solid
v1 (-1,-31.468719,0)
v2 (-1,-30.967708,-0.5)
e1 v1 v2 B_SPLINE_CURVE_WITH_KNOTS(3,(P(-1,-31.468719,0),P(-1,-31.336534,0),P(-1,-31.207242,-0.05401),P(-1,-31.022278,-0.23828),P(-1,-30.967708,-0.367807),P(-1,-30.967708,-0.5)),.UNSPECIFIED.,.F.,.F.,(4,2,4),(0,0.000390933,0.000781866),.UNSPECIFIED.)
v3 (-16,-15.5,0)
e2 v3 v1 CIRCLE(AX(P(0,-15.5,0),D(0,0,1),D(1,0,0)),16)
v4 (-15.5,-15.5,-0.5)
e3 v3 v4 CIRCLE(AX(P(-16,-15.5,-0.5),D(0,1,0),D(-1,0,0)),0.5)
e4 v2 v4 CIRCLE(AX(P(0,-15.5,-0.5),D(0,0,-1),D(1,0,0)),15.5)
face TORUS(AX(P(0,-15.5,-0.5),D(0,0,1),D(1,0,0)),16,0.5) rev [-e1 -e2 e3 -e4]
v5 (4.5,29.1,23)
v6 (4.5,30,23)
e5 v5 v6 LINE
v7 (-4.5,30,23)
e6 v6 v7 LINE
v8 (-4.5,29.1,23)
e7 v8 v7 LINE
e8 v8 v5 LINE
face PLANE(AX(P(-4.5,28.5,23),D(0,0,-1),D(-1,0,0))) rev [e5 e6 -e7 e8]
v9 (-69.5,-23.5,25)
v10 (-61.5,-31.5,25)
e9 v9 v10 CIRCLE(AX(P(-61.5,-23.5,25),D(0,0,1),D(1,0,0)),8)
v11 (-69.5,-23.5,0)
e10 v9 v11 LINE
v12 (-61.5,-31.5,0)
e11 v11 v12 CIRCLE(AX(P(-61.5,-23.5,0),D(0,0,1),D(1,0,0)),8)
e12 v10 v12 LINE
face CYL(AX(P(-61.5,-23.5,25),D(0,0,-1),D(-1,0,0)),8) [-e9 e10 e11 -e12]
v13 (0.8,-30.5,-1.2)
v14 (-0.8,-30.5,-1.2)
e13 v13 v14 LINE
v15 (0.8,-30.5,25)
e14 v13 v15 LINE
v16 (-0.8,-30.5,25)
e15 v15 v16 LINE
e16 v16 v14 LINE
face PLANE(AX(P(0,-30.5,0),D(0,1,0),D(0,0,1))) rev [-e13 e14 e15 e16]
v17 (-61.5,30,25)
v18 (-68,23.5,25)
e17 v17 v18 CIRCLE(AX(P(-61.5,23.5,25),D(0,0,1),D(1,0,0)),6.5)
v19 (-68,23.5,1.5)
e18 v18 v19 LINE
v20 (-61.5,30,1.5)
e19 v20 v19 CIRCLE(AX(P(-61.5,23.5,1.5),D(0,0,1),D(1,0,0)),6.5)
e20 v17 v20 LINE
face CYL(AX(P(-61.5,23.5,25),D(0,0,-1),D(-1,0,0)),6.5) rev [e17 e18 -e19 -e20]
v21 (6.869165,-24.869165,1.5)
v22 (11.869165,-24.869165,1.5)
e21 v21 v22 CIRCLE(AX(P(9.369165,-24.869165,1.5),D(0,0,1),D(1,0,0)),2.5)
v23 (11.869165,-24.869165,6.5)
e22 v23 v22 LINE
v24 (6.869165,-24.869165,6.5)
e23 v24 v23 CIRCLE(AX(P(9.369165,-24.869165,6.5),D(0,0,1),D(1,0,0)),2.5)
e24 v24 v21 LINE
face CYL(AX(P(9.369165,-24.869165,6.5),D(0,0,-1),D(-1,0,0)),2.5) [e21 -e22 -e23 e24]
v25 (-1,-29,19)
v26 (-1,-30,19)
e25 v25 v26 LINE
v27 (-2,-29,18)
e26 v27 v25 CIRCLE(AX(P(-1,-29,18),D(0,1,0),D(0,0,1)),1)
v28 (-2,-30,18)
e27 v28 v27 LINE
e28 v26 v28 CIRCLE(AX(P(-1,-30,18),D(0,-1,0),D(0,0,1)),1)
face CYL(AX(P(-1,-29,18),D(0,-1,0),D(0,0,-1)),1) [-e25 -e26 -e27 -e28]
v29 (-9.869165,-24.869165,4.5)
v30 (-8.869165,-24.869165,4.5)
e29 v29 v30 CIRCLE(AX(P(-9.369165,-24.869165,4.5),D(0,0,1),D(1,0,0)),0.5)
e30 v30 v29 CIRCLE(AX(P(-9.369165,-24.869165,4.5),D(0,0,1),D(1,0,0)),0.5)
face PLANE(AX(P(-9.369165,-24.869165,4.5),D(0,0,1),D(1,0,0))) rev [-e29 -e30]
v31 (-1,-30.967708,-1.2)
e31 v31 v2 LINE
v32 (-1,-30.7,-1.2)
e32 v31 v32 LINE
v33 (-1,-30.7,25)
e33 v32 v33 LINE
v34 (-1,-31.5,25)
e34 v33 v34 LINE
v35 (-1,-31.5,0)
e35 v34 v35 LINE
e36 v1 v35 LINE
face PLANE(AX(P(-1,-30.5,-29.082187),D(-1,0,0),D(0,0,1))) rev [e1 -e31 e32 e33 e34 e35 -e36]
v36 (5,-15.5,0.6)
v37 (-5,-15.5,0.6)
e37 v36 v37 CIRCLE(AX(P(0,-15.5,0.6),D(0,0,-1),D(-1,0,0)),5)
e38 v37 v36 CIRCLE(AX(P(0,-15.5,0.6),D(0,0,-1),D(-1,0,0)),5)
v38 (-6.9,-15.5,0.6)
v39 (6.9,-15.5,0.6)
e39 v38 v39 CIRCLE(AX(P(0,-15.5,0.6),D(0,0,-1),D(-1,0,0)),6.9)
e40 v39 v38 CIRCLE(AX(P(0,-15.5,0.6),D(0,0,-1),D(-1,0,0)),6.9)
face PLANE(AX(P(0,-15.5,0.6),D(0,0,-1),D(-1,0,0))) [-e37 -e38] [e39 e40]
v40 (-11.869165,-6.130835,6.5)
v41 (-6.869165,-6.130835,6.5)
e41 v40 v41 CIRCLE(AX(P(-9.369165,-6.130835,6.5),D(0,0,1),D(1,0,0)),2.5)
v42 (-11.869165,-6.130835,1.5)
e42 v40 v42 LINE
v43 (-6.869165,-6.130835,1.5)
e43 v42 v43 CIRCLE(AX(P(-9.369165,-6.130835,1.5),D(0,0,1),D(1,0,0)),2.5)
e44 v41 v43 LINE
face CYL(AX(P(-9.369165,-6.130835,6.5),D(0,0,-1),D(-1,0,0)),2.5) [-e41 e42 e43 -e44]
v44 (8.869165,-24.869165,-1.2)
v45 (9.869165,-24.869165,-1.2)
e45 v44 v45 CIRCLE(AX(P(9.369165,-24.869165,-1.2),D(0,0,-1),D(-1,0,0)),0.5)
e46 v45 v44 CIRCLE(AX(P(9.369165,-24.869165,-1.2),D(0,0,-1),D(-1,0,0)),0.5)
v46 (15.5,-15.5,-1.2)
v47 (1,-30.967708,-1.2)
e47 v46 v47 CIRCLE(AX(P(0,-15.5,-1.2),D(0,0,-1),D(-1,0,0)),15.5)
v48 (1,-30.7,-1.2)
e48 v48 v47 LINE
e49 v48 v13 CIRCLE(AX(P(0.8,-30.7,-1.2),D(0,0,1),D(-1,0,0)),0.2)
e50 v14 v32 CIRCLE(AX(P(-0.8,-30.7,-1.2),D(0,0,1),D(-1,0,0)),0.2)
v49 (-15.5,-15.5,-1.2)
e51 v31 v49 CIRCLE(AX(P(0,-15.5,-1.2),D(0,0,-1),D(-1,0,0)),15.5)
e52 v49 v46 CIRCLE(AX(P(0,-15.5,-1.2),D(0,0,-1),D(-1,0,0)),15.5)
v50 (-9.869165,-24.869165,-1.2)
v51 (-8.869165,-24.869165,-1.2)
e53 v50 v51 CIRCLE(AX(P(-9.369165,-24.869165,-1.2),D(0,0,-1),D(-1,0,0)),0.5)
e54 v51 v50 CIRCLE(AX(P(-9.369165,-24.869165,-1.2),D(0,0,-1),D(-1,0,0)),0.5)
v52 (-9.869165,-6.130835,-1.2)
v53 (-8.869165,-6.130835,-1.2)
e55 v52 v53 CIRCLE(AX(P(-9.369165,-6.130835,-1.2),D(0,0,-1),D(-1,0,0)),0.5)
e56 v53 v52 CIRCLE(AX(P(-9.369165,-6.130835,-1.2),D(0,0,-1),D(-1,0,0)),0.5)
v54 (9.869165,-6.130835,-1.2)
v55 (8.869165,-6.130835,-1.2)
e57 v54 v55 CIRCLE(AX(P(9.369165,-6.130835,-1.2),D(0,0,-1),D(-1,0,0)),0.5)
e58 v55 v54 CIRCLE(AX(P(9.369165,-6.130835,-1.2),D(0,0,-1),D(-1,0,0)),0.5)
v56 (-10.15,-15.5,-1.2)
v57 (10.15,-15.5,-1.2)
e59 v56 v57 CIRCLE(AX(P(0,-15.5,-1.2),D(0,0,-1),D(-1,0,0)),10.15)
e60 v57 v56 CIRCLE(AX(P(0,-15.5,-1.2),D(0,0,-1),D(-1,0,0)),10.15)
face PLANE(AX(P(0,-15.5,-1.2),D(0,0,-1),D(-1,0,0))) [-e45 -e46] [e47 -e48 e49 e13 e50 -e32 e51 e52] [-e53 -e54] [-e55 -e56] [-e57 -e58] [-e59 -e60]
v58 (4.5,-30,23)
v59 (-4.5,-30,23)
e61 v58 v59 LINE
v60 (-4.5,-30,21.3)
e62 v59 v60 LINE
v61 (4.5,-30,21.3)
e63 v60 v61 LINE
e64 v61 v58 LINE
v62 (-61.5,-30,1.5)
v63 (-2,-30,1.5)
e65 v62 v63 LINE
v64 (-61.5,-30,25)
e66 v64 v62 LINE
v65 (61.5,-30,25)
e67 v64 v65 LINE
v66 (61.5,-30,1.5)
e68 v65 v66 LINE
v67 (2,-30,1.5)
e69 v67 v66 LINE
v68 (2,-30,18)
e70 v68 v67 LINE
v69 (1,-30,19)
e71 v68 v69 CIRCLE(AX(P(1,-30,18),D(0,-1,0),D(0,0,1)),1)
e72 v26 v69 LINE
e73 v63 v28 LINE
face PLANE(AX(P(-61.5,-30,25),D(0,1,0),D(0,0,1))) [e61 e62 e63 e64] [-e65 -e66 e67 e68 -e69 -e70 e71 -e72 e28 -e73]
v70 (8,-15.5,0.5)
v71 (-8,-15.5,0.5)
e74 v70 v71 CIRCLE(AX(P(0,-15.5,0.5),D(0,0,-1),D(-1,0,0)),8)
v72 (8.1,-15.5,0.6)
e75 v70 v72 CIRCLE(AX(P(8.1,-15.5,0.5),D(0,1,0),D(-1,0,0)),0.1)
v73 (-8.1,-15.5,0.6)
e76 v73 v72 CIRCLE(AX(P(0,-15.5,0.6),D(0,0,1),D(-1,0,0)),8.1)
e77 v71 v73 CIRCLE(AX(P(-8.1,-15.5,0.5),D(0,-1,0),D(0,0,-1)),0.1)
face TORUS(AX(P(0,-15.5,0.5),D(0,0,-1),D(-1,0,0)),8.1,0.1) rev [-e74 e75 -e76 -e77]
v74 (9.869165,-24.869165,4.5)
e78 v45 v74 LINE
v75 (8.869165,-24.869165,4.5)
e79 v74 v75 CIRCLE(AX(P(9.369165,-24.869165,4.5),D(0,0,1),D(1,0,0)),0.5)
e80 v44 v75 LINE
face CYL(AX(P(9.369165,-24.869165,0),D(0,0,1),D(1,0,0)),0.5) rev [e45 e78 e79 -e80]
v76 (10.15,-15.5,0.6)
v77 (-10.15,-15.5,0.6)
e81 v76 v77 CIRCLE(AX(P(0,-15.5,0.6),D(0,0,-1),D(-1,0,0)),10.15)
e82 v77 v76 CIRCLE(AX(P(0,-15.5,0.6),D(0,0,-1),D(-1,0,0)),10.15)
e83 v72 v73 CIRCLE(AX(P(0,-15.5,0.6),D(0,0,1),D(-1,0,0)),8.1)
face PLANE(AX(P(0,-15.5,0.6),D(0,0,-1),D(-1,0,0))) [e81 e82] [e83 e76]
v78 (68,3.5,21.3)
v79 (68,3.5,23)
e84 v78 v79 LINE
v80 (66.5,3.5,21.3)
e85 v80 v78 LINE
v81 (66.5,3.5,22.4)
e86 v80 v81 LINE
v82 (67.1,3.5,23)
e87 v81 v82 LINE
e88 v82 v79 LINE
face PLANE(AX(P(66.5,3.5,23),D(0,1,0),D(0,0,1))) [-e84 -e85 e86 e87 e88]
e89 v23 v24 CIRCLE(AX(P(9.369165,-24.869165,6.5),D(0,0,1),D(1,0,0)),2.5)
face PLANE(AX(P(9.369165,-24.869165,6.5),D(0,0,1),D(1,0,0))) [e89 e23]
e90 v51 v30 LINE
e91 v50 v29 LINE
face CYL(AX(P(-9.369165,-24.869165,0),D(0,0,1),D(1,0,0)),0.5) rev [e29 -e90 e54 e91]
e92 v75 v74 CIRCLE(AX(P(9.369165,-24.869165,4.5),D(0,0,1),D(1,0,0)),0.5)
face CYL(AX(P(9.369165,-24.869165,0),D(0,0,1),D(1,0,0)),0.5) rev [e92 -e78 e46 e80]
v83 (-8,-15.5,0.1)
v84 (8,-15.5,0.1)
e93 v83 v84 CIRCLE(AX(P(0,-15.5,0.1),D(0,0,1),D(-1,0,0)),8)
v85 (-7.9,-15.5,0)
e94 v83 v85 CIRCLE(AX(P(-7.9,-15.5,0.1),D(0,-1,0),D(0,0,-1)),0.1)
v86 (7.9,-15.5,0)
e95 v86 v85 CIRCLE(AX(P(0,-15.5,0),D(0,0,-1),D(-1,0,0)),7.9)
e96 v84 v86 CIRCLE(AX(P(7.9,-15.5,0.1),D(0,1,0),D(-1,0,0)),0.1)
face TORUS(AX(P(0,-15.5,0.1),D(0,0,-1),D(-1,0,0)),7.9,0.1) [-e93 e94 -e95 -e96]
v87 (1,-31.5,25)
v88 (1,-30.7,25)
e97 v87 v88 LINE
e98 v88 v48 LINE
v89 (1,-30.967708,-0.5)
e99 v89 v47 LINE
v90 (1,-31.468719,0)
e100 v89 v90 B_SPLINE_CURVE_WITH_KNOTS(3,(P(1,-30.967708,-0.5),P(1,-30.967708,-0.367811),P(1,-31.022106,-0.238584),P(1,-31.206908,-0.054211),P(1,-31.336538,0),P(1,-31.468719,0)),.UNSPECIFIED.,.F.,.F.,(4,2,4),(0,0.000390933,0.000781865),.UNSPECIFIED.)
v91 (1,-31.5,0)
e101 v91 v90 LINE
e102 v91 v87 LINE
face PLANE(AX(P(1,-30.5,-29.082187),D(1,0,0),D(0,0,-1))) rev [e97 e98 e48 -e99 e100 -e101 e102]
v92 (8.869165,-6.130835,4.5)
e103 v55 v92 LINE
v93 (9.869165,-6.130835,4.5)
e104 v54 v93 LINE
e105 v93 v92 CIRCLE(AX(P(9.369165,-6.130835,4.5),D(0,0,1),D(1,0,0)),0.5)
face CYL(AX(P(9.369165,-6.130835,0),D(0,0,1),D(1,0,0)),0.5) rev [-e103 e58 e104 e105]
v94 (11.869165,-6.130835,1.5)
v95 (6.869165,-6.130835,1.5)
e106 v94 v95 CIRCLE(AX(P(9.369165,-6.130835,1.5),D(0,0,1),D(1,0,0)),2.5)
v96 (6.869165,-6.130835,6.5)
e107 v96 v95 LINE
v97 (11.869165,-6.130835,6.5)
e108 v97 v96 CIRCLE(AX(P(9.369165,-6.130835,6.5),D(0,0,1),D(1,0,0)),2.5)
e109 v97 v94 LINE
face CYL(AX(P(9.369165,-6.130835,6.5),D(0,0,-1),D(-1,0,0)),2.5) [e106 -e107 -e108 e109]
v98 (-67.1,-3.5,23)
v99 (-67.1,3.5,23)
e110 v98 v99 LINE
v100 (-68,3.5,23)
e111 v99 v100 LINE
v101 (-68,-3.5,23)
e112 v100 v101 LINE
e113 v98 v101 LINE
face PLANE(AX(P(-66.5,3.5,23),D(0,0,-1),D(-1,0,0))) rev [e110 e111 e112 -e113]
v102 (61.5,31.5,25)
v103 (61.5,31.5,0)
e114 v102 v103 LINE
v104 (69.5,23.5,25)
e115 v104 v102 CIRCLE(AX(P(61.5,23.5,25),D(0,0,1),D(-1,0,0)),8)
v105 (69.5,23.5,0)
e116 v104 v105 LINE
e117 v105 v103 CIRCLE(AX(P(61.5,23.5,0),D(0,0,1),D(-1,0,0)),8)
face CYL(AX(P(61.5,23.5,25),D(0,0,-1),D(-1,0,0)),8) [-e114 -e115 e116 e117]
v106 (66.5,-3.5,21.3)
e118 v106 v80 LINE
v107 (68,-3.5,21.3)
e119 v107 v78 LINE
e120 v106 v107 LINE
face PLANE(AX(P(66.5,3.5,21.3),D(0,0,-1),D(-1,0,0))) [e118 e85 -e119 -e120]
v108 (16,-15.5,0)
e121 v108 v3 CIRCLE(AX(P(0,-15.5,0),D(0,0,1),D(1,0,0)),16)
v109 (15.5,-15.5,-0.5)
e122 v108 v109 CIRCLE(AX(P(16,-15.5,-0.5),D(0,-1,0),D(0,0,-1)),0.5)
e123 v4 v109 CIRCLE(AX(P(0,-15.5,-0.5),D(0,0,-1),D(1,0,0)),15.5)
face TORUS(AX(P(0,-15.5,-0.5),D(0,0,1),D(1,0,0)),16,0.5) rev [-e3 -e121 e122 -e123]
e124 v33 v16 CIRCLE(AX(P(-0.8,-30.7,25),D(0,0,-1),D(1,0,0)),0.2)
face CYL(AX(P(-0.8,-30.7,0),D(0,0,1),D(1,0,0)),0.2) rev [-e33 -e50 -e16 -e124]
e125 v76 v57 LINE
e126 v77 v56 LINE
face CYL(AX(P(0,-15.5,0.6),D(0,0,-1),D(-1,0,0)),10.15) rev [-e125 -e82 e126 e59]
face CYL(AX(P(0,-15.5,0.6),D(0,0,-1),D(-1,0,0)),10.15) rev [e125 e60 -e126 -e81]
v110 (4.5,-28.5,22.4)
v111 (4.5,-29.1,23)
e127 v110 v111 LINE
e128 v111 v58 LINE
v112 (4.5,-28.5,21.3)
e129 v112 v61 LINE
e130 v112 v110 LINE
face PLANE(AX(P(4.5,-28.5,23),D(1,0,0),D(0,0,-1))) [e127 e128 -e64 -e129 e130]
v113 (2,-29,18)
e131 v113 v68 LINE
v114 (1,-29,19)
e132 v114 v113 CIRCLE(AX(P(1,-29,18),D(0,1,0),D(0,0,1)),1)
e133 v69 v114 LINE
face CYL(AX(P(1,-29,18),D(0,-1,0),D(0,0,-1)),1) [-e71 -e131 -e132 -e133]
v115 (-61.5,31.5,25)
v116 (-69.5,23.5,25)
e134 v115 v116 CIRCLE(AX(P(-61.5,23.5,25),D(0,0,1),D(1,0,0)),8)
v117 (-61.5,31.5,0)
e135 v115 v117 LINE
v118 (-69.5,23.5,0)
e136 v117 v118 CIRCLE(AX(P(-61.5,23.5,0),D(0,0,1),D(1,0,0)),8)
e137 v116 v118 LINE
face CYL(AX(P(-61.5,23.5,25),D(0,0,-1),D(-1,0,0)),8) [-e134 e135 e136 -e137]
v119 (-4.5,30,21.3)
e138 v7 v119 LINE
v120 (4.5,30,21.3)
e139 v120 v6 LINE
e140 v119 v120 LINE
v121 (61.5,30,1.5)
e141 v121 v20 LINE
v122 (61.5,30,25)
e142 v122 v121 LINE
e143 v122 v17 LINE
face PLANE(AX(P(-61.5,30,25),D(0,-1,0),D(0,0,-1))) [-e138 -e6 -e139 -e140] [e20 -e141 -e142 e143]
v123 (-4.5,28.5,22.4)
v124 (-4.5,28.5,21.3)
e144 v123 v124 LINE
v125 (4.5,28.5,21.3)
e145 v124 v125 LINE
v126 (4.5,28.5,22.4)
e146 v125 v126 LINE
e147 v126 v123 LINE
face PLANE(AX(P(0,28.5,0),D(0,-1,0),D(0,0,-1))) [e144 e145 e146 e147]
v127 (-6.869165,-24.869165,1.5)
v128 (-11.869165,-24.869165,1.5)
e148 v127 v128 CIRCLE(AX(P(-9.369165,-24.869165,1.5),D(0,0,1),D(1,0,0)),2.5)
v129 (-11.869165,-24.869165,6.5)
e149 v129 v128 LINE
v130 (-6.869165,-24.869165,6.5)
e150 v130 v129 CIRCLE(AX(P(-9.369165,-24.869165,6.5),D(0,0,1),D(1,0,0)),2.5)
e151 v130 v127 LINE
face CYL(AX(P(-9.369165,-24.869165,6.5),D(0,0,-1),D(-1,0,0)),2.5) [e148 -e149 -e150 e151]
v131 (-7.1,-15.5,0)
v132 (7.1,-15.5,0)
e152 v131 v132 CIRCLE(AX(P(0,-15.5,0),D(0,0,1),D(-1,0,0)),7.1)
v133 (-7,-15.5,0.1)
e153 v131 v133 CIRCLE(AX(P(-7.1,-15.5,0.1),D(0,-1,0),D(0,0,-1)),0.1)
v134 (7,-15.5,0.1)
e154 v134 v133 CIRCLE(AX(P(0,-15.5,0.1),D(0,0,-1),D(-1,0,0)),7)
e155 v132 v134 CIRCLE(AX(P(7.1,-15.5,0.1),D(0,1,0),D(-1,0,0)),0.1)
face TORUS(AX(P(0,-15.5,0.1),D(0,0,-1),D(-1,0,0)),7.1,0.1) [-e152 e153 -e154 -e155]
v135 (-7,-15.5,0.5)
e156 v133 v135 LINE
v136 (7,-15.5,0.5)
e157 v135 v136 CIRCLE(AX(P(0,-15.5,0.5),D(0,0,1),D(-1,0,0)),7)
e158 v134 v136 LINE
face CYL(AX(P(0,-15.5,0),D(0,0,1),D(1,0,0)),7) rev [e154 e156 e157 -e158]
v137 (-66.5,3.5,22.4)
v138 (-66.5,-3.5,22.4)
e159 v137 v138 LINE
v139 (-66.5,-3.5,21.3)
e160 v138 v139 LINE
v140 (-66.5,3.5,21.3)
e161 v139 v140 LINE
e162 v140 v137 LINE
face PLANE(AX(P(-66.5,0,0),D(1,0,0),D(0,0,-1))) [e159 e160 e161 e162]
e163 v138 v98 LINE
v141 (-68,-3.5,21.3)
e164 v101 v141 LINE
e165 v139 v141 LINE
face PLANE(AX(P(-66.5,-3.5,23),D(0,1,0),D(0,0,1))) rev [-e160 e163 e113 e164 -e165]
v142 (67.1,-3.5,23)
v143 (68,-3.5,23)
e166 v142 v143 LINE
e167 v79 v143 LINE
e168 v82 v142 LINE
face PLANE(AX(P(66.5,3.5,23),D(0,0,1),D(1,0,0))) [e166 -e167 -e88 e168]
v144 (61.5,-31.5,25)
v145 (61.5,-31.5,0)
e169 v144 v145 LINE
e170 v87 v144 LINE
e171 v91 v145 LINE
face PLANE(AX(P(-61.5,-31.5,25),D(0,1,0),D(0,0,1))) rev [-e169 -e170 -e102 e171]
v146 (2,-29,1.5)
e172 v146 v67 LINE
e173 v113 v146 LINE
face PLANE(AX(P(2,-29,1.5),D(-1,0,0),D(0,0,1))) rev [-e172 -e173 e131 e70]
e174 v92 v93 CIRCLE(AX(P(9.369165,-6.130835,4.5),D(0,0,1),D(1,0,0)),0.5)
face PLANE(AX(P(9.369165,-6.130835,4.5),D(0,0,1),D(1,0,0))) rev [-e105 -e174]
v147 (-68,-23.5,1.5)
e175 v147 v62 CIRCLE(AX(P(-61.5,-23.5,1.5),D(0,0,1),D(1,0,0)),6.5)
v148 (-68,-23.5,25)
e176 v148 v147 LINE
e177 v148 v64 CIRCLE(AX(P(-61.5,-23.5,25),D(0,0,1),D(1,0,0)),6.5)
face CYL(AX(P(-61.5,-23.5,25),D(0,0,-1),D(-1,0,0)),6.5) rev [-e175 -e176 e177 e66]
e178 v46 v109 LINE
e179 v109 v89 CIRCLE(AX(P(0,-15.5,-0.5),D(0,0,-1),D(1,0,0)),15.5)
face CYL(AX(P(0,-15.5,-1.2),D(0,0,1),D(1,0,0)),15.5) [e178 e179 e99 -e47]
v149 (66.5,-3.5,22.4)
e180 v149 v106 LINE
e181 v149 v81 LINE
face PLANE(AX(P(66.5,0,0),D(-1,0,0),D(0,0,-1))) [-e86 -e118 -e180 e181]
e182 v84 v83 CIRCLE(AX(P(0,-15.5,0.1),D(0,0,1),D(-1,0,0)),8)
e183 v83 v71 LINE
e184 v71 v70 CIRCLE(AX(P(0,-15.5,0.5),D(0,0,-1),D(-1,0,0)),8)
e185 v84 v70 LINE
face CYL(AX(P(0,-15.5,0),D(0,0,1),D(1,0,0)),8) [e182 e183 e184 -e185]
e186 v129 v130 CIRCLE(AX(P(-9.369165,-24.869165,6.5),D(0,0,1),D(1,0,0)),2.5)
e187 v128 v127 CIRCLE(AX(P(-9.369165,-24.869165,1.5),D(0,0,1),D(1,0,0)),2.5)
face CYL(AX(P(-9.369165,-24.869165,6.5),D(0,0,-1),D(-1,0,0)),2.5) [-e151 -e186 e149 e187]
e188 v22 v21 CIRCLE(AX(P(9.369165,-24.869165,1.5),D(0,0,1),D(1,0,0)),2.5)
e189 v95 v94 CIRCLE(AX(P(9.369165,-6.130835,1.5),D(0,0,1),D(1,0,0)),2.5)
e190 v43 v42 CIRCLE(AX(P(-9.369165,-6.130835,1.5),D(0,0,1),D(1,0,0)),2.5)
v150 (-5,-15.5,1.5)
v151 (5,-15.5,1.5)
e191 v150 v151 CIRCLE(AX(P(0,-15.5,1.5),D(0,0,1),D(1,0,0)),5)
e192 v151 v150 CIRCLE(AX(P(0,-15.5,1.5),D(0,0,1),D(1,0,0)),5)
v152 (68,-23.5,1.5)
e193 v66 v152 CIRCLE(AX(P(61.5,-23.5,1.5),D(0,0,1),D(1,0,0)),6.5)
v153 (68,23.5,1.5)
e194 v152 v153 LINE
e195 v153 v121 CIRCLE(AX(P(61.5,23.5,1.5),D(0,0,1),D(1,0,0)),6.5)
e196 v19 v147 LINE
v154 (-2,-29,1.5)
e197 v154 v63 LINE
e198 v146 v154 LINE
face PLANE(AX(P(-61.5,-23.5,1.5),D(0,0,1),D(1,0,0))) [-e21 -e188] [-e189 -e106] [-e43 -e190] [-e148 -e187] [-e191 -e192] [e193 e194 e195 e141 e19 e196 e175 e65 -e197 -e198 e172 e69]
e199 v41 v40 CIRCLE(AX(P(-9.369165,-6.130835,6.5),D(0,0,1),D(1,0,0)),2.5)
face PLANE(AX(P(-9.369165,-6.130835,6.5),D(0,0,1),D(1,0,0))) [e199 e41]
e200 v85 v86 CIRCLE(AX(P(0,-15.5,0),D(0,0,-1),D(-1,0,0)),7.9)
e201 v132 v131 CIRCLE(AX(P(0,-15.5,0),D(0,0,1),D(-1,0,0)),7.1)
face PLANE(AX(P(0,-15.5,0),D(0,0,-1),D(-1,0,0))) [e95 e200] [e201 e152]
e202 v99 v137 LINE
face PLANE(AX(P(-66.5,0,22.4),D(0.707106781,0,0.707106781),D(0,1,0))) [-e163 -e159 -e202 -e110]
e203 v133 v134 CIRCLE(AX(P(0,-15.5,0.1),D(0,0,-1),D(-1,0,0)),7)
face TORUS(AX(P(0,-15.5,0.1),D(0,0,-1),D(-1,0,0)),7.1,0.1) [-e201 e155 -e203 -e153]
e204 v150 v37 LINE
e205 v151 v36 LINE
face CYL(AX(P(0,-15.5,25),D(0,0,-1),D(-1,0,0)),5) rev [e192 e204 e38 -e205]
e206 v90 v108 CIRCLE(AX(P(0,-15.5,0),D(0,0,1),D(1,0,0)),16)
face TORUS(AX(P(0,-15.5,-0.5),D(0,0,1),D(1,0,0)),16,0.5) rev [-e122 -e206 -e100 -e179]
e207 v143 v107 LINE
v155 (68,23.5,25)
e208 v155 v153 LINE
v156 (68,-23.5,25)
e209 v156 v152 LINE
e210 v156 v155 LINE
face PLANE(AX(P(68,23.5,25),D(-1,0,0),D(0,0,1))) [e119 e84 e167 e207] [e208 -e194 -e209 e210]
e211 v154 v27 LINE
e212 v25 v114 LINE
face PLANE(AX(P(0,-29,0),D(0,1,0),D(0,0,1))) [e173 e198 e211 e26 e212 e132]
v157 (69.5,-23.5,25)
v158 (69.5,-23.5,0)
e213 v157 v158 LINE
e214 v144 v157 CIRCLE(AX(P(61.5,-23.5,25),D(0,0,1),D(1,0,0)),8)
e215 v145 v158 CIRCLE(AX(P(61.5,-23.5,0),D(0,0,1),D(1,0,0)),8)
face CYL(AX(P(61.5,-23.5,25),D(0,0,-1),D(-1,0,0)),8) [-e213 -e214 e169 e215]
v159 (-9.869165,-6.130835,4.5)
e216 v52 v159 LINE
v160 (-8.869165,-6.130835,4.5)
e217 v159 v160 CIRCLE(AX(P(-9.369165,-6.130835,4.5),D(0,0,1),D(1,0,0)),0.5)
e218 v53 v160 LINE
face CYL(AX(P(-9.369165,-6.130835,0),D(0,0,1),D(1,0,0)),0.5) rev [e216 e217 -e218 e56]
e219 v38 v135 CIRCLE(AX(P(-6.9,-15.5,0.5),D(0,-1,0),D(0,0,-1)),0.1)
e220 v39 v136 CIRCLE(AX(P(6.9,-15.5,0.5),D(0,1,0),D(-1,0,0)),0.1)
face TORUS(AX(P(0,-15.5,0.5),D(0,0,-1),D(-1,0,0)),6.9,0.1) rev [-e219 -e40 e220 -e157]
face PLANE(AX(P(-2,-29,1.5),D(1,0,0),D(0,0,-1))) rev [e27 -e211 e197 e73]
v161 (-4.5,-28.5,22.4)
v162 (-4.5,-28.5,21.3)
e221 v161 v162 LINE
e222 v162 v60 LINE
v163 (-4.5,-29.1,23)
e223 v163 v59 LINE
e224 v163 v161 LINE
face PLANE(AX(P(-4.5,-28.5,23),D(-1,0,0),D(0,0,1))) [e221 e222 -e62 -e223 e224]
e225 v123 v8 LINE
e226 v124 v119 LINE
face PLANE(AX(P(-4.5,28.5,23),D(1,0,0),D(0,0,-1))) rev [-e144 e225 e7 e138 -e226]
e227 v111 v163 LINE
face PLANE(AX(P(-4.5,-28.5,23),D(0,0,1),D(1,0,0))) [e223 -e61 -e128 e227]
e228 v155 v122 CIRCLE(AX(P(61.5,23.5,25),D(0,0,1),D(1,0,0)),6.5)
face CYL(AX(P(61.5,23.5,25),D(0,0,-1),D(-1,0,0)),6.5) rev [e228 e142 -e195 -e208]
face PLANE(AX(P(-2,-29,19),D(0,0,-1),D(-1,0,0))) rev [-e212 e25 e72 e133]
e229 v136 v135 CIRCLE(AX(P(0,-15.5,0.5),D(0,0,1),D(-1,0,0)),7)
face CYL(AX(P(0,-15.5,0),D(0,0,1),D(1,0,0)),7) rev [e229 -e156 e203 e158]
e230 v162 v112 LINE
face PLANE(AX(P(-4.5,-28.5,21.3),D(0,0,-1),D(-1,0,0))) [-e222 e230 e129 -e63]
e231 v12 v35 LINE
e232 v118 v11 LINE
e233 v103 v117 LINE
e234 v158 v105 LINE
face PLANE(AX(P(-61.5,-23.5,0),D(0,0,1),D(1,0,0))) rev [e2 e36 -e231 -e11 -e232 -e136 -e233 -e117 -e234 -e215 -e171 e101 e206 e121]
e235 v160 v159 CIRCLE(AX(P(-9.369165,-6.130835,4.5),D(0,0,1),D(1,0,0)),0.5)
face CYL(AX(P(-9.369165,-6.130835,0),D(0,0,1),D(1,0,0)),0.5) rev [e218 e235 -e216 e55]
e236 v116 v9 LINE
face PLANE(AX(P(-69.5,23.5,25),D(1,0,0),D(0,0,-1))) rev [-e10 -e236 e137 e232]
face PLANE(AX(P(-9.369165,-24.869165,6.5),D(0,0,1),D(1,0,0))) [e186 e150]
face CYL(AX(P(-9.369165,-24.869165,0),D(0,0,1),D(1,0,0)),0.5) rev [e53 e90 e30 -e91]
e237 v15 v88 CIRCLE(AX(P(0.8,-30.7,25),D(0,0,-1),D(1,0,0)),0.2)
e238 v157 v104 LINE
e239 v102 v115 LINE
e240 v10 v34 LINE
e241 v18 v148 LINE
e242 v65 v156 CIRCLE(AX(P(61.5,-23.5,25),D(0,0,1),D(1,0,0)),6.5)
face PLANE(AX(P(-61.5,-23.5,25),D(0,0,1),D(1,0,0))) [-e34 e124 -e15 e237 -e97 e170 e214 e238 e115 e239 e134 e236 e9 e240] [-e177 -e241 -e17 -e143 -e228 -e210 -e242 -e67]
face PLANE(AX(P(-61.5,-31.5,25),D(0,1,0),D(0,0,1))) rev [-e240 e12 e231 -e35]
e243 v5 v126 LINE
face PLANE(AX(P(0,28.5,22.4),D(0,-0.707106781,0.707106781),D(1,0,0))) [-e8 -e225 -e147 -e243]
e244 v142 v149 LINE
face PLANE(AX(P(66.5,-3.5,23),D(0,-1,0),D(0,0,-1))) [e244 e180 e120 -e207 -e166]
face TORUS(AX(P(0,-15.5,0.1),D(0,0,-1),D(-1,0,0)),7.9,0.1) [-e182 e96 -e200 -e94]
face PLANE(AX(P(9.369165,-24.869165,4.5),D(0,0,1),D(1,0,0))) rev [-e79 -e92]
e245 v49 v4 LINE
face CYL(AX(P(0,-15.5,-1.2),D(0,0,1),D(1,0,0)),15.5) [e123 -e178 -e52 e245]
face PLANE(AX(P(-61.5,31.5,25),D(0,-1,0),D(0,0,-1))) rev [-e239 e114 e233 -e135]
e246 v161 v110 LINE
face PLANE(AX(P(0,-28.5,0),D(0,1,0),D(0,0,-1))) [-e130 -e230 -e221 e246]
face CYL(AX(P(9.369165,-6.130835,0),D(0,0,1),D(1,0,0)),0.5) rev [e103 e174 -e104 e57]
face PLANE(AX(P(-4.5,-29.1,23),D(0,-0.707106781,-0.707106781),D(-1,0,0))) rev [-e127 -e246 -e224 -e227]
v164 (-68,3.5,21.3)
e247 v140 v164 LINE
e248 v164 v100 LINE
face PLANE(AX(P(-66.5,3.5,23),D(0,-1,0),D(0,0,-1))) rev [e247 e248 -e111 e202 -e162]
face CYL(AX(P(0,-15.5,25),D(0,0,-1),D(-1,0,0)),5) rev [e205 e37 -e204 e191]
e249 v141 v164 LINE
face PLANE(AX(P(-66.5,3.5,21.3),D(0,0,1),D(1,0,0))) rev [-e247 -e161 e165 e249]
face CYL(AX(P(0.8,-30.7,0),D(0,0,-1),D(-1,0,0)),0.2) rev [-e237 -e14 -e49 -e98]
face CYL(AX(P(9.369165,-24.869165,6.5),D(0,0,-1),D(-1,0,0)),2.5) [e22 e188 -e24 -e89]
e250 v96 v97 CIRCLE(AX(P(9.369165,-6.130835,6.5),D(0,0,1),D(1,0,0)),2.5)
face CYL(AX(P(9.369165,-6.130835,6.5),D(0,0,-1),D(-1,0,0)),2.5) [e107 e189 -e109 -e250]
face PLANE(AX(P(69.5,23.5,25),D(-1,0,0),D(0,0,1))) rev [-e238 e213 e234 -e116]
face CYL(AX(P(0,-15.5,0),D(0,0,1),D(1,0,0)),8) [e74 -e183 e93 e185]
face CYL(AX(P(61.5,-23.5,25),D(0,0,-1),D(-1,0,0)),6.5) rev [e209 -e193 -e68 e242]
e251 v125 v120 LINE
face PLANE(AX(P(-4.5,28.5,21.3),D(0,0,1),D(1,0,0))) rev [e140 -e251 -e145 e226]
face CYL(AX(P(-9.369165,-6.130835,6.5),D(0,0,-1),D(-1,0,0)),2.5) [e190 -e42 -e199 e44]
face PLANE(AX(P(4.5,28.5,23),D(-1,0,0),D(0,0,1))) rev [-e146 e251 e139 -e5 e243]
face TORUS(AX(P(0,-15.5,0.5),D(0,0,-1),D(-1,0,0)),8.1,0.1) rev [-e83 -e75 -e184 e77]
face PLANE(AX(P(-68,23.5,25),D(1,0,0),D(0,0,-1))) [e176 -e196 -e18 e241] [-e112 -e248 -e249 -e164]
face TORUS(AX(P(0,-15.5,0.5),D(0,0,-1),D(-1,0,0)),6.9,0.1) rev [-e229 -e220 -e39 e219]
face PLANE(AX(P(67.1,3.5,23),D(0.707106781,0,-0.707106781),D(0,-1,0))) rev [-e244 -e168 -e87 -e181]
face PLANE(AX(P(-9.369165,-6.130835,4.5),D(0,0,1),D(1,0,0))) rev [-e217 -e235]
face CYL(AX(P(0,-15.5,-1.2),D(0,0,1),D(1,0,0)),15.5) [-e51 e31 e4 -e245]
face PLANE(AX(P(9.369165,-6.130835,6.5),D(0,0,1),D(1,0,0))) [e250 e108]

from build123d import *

# Parameters (mm, degrees)
BOSS_EXTRUDE1_DEPTH      = 25
SHELL1_T                 = -1.5
SKETCH2_W                = 9
SKETCH2_H                = 1.7
BOSS_EXTRUDE2_DEPTH      = 1.5
CHAMFER1_SIZE            = 0.6
CHAMFER1_OF_MIRROR1_SIZE = 0.6
SKETCH3_W                = 4
SKETCH3_H                = 17.5
BOSS_EXTRUDE3_DEPTH      = 1
SKETCH6_R                = 10.15
CUT_EXTRUDE3_DEPTH       = 0.6
SKETCH10_R               = 5
CUT_EXTRUDE4_DEPTH       = 81.111547233
SKETCH11_R               = 8
SKETCH11_R_2             = 7
BOSS_EXTRUDE5_DEPTH      = 0.6
SKETCH13_R               = 2.5
BOSS_EXTRUDE6_DEPTH      = 5
CUT_EXTRUDE5_START       = -2
SKETCH15_R               = 0.5
CUT_EXTRUDE5_DEPTH       = 77.515921952
SKETCH16_W               = 2
SKETCH16_H               = 58.164373892
CUT_EXTRUDE6_DEPTH       = 1
FILLET2_R                = 0.1
SKETCH17_R               = 15.5
SKETCH17_R_2             = 10.15
SKETCH17_R_3             = 0.5
BOSS_EXTRUDE7_DEPTH      = 1.2
SKETCH18_W               = 2
SKETCH18_H               = 1.626209188
CUT_EXTRUDE7_DEPTH       = 1
FILLET3_R                = 0.5
FILLET4_R                = 1
SKETCH19_W               = 1.7
SKETCH19_H               = 7
BOSS_EXTRUDE8_DEPTH      = 1.5
CHAMFER2_SIZE            = 0.6
CHAMFER2_OF_MIRROR2_SIZE = 0.6
FILLET5_R                = 0.2


with BuildPart() as part:
    # Sketch1 → Boss-Extrude1 (new body)
    with BuildSketch(Plane.XY):
        with BuildLine():
            Line((-61.5, 31.5), (61.5, 31.5))
            ThreePointArc((61.5, 31.5), (67.156854249, 29.156854249), (69.5, 23.5))
            Line((69.5, 23.5), (69.5, -23.5))
            ThreePointArc((69.5, -23.5), (67.156854249, -29.156854249), (61.5, -31.5))
            Line((61.5, -31.5), (-61.5, -31.5))
            ThreePointArc((-61.5, -31.5), (-67.156854249, -29.156854249), (-69.5, -23.5))
            Line((-69.5, -23.5), (-69.5, 23.5))
            ThreePointArc((-69.5, 23.5), (-67.156854249, 29.156854249), (-61.5, 31.5))
        make_face()
    extrude(amount=BOSS_EXTRUDE1_DEPTH)

    # Shell1
    shell1_openings = [part.faces().sort_by_distance(p)[0] for p in [
        (0, 0, 25),
    ]]
    offset(amount=SHELL1_T, openings=shell1_openings, kind=Kind.INTERSECTION)

    # Sketch2 → Boss-Extrude2 (add)
    with BuildSketch(Plane(origin=(0, 30, 0), x_dir=(-1, 0, 0), z_dir=(0, -1, 0))):
        with Locations((0, -22.15)):
            Rectangle(SKETCH2_W, SKETCH2_H)
    boss_extrude2 = extrude(amount=BOSS_EXTRUDE2_DEPTH)

    # Chamfer1
    chamfer1_edges = [part.edges().sort_by_distance(p)[0] for p in [
        (0, 28.5, 23),
    ]]
    chamfer(chamfer1_edges, length=CHAMFER1_SIZE)

    # Mirror1: Boss-Extrude2 across plane
    add(boss_extrude2.mirror(Plane.ZX))

    # Chamfer1 of Mirror1
    chamfer1_of_mirror1_edges = [part.edges().sort_by_distance(p)[0] for p in [
        (0, -28.5, 23),
    ]]
    chamfer(chamfer1_of_mirror1_edges, length=CHAMFER1_OF_MIRROR1_SIZE)

    # Sketch3 → Boss-Extrude3 (add)
    with BuildSketch(Plane(origin=(0, -30, 0), x_dir=(1, 0, 0), z_dir=(0, 1, 0))):
        with Locations((0, -10.25)):
            Rectangle(SKETCH3_W, SKETCH3_H)
    extrude(amount=BOSS_EXTRUDE3_DEPTH)

    # Sketch6 → Cut-Extrude3 (cut)
    with BuildSketch(Plane(origin=(0, 0, 0), x_dir=(-1, 0, 0), z_dir=(0, 0, -1))):
        with Locations((0, -15.5)):
            Circle(SKETCH6_R)
    extrude(amount=-CUT_EXTRUDE3_DEPTH, mode=Mode.SUBTRACT)

    # Sketch10 → Cut-Extrude4 (cut, through all)
    with BuildSketch(Plane(origin=(0, 0, 0.6), x_dir=(-1, 0, 0), z_dir=(0, 0, -1))):
        with Locations((0, -15.5)):
            Circle(SKETCH10_R)
    extrude(amount=-CUT_EXTRUDE4_DEPTH, mode=Mode.SUBTRACT)

    # Sketch11 → Boss-Extrude5 (add)
    with BuildSketch(Plane(origin=(0, 0, 0.6), x_dir=(-1, 0, 0), z_dir=(0, 0, -1))):
        with Locations((0, -15.5)):
            Circle(SKETCH11_R)
        with Locations((0, -15.5)):
            Circle(SKETCH11_R_2, mode=Mode.SUBTRACT)
    extrude(amount=BOSS_EXTRUDE5_DEPTH)

    # Sketch13 → Boss-Extrude6 (add)
    with BuildSketch(Plane.XY.offset(1.5)):
        with Locations((-9.369164851, -6.130835149)):
            Circle(SKETCH13_R)
        with Locations((9.369164851, -6.130835149)):
            Circle(SKETCH13_R)
        with Locations((9.369164851, -24.869164851)):
            Circle(SKETCH13_R)
        with Locations((-9.369164851, -24.869164851)):
            Circle(SKETCH13_R)
    extrude(amount=BOSS_EXTRUDE6_DEPTH)

    # Sketch15 → Cut-Extrude5 (cut, through all)
    with BuildSketch(Plane.XY.offset(6.5).offset(CUT_EXTRUDE5_START)):
        with Locations((9.369164851, -6.130835149)):
            Circle(SKETCH15_R)
        with Locations((-9.369164851, -6.130835149)):
            Circle(SKETCH15_R)
        with Locations((-9.369164851, -24.869164851)):
            Circle(SKETCH15_R)
        with Locations((9.369164851, -24.869164851)):
            Circle(SKETCH15_R)
    extrude(amount=-CUT_EXTRUDE5_DEPTH, mode=Mode.SUBTRACT)

    # Sketch16 → Cut-Extrude6 (cut)
    with BuildSketch(Plane(origin=(0, -31.5, 0), x_dir=(-1, 0, 0), z_dir=(0, -1, 0))):
        Rectangle(SKETCH16_W, SKETCH16_H)
    extrude(amount=-CUT_EXTRUDE6_DEPTH, mode=Mode.SUBTRACT)

    # Fillet2
    fillet2_edges = [part.edges().sort_by_distance(p)[0] for p in [
        (7, -15.5, 0.6),
        (8, -15.5, 0),
        (8, -15.5, 0.6),
        (7, -15.5, 0),
    ]]
    fillet(fillet2_edges, radius=FILLET2_R)

    # Sketch17 → Boss-Extrude7 (add)
    with BuildSketch(Plane(origin=(0, 0, 0), x_dir=(-1, 0, 0), z_dir=(0, 0, -1))):
        with Locations(Location((0, -15.5, 0), (0, 0, 266.300928937))):
            Circle(SKETCH17_R)
        with Locations((0, -15.5)):
            Circle(SKETCH17_R_2, mode=Mode.SUBTRACT)
        with Locations(Location((-9.369164851, -6.130835149, 0), (0, 0, 180))):
            Circle(SKETCH17_R_3, mode=Mode.SUBTRACT)
        with Locations(Location((9.369164851, -6.130835149, 0), (0, 0, 180))):
            Circle(SKETCH17_R_3, mode=Mode.SUBTRACT)
        with Locations(Location((9.369164851, -24.869164851, 0), (0, 0, 180))):
            Circle(SKETCH17_R_3, mode=Mode.SUBTRACT)
        with Locations(Location((-9.369164851, -24.869164851, 0), (0, 0, 180))):
            Circle(SKETCH17_R_3, mode=Mode.SUBTRACT)
    extrude(amount=BOSS_EXTRUDE7_DEPTH)

    # Sketch18 → Cut-Extrude7 (cut)
    with BuildSketch(Plane(origin=(0, -31.5, 0), x_dir=(-1, 0, 0), z_dir=(0, -1, 0))):
        with Locations((0, 0.813104594)):
            Rectangle(SKETCH18_W, SKETCH18_H)
    extrude(amount=-CUT_EXTRUDE7_DEPTH, mode=Mode.SUBTRACT)

    # Fillet3
    fillet3_edges = [part.edges().sort_by_distance(p)[0] for p in [
        (0, 0, 0),
    ]]
    fillet(fillet3_edges, radius=FILLET3_R)

    # Fillet4
    fillet4_edges = [part.edges().sort_by_distance(p)[0] for p in [
        (-2, -29.5, 19),
        (2, -29.5, 19),
    ]]
    fillet(fillet4_edges, radius=FILLET4_R)

    # Sketch19 → Boss-Extrude8 (add)
    with BuildSketch(Plane(origin=(-68, 0, 0), x_dir=(0, 0, -1), z_dir=(1, 0, 0))):
        with Locations((-22.15, 0)):
            Rectangle(SKETCH19_W, SKETCH19_H)
    boss_extrude8 = extrude(amount=BOSS_EXTRUDE8_DEPTH)

    # Chamfer2
    chamfer2_edges = [part.edges().sort_by_distance(p)[0] for p in [
        (-66.5, 0, 23),
    ]]
    chamfer(chamfer2_edges, length=CHAMFER2_SIZE)

    # Mirror2: Boss-Extrude8 across plane
    add(boss_extrude8.mirror(Plane(origin=(0, 0, 0), x_dir=(0, 0, 1), z_dir=(1, 0, 0))))

    # Chamfer2 of Mirror2
    chamfer2_of_mirror2_edges = [part.edges().sort_by_distance(p)[0] for p in [
        (66.5, 0, 23),
    ]]
    chamfer(chamfer2_of_mirror2_edges, length=CHAMFER2_OF_MIRROR2_SIZE)

    # Fillet5
    fillet5_edges = [part.edges().sort_by_distance(p)[0] for p in [
        (1, -30.5, 11.9),
        (-1, -30.5, 11.9),
    ]]
    fillet(fillet5_edges, radius=FILLET5_R)


solid = part.part
